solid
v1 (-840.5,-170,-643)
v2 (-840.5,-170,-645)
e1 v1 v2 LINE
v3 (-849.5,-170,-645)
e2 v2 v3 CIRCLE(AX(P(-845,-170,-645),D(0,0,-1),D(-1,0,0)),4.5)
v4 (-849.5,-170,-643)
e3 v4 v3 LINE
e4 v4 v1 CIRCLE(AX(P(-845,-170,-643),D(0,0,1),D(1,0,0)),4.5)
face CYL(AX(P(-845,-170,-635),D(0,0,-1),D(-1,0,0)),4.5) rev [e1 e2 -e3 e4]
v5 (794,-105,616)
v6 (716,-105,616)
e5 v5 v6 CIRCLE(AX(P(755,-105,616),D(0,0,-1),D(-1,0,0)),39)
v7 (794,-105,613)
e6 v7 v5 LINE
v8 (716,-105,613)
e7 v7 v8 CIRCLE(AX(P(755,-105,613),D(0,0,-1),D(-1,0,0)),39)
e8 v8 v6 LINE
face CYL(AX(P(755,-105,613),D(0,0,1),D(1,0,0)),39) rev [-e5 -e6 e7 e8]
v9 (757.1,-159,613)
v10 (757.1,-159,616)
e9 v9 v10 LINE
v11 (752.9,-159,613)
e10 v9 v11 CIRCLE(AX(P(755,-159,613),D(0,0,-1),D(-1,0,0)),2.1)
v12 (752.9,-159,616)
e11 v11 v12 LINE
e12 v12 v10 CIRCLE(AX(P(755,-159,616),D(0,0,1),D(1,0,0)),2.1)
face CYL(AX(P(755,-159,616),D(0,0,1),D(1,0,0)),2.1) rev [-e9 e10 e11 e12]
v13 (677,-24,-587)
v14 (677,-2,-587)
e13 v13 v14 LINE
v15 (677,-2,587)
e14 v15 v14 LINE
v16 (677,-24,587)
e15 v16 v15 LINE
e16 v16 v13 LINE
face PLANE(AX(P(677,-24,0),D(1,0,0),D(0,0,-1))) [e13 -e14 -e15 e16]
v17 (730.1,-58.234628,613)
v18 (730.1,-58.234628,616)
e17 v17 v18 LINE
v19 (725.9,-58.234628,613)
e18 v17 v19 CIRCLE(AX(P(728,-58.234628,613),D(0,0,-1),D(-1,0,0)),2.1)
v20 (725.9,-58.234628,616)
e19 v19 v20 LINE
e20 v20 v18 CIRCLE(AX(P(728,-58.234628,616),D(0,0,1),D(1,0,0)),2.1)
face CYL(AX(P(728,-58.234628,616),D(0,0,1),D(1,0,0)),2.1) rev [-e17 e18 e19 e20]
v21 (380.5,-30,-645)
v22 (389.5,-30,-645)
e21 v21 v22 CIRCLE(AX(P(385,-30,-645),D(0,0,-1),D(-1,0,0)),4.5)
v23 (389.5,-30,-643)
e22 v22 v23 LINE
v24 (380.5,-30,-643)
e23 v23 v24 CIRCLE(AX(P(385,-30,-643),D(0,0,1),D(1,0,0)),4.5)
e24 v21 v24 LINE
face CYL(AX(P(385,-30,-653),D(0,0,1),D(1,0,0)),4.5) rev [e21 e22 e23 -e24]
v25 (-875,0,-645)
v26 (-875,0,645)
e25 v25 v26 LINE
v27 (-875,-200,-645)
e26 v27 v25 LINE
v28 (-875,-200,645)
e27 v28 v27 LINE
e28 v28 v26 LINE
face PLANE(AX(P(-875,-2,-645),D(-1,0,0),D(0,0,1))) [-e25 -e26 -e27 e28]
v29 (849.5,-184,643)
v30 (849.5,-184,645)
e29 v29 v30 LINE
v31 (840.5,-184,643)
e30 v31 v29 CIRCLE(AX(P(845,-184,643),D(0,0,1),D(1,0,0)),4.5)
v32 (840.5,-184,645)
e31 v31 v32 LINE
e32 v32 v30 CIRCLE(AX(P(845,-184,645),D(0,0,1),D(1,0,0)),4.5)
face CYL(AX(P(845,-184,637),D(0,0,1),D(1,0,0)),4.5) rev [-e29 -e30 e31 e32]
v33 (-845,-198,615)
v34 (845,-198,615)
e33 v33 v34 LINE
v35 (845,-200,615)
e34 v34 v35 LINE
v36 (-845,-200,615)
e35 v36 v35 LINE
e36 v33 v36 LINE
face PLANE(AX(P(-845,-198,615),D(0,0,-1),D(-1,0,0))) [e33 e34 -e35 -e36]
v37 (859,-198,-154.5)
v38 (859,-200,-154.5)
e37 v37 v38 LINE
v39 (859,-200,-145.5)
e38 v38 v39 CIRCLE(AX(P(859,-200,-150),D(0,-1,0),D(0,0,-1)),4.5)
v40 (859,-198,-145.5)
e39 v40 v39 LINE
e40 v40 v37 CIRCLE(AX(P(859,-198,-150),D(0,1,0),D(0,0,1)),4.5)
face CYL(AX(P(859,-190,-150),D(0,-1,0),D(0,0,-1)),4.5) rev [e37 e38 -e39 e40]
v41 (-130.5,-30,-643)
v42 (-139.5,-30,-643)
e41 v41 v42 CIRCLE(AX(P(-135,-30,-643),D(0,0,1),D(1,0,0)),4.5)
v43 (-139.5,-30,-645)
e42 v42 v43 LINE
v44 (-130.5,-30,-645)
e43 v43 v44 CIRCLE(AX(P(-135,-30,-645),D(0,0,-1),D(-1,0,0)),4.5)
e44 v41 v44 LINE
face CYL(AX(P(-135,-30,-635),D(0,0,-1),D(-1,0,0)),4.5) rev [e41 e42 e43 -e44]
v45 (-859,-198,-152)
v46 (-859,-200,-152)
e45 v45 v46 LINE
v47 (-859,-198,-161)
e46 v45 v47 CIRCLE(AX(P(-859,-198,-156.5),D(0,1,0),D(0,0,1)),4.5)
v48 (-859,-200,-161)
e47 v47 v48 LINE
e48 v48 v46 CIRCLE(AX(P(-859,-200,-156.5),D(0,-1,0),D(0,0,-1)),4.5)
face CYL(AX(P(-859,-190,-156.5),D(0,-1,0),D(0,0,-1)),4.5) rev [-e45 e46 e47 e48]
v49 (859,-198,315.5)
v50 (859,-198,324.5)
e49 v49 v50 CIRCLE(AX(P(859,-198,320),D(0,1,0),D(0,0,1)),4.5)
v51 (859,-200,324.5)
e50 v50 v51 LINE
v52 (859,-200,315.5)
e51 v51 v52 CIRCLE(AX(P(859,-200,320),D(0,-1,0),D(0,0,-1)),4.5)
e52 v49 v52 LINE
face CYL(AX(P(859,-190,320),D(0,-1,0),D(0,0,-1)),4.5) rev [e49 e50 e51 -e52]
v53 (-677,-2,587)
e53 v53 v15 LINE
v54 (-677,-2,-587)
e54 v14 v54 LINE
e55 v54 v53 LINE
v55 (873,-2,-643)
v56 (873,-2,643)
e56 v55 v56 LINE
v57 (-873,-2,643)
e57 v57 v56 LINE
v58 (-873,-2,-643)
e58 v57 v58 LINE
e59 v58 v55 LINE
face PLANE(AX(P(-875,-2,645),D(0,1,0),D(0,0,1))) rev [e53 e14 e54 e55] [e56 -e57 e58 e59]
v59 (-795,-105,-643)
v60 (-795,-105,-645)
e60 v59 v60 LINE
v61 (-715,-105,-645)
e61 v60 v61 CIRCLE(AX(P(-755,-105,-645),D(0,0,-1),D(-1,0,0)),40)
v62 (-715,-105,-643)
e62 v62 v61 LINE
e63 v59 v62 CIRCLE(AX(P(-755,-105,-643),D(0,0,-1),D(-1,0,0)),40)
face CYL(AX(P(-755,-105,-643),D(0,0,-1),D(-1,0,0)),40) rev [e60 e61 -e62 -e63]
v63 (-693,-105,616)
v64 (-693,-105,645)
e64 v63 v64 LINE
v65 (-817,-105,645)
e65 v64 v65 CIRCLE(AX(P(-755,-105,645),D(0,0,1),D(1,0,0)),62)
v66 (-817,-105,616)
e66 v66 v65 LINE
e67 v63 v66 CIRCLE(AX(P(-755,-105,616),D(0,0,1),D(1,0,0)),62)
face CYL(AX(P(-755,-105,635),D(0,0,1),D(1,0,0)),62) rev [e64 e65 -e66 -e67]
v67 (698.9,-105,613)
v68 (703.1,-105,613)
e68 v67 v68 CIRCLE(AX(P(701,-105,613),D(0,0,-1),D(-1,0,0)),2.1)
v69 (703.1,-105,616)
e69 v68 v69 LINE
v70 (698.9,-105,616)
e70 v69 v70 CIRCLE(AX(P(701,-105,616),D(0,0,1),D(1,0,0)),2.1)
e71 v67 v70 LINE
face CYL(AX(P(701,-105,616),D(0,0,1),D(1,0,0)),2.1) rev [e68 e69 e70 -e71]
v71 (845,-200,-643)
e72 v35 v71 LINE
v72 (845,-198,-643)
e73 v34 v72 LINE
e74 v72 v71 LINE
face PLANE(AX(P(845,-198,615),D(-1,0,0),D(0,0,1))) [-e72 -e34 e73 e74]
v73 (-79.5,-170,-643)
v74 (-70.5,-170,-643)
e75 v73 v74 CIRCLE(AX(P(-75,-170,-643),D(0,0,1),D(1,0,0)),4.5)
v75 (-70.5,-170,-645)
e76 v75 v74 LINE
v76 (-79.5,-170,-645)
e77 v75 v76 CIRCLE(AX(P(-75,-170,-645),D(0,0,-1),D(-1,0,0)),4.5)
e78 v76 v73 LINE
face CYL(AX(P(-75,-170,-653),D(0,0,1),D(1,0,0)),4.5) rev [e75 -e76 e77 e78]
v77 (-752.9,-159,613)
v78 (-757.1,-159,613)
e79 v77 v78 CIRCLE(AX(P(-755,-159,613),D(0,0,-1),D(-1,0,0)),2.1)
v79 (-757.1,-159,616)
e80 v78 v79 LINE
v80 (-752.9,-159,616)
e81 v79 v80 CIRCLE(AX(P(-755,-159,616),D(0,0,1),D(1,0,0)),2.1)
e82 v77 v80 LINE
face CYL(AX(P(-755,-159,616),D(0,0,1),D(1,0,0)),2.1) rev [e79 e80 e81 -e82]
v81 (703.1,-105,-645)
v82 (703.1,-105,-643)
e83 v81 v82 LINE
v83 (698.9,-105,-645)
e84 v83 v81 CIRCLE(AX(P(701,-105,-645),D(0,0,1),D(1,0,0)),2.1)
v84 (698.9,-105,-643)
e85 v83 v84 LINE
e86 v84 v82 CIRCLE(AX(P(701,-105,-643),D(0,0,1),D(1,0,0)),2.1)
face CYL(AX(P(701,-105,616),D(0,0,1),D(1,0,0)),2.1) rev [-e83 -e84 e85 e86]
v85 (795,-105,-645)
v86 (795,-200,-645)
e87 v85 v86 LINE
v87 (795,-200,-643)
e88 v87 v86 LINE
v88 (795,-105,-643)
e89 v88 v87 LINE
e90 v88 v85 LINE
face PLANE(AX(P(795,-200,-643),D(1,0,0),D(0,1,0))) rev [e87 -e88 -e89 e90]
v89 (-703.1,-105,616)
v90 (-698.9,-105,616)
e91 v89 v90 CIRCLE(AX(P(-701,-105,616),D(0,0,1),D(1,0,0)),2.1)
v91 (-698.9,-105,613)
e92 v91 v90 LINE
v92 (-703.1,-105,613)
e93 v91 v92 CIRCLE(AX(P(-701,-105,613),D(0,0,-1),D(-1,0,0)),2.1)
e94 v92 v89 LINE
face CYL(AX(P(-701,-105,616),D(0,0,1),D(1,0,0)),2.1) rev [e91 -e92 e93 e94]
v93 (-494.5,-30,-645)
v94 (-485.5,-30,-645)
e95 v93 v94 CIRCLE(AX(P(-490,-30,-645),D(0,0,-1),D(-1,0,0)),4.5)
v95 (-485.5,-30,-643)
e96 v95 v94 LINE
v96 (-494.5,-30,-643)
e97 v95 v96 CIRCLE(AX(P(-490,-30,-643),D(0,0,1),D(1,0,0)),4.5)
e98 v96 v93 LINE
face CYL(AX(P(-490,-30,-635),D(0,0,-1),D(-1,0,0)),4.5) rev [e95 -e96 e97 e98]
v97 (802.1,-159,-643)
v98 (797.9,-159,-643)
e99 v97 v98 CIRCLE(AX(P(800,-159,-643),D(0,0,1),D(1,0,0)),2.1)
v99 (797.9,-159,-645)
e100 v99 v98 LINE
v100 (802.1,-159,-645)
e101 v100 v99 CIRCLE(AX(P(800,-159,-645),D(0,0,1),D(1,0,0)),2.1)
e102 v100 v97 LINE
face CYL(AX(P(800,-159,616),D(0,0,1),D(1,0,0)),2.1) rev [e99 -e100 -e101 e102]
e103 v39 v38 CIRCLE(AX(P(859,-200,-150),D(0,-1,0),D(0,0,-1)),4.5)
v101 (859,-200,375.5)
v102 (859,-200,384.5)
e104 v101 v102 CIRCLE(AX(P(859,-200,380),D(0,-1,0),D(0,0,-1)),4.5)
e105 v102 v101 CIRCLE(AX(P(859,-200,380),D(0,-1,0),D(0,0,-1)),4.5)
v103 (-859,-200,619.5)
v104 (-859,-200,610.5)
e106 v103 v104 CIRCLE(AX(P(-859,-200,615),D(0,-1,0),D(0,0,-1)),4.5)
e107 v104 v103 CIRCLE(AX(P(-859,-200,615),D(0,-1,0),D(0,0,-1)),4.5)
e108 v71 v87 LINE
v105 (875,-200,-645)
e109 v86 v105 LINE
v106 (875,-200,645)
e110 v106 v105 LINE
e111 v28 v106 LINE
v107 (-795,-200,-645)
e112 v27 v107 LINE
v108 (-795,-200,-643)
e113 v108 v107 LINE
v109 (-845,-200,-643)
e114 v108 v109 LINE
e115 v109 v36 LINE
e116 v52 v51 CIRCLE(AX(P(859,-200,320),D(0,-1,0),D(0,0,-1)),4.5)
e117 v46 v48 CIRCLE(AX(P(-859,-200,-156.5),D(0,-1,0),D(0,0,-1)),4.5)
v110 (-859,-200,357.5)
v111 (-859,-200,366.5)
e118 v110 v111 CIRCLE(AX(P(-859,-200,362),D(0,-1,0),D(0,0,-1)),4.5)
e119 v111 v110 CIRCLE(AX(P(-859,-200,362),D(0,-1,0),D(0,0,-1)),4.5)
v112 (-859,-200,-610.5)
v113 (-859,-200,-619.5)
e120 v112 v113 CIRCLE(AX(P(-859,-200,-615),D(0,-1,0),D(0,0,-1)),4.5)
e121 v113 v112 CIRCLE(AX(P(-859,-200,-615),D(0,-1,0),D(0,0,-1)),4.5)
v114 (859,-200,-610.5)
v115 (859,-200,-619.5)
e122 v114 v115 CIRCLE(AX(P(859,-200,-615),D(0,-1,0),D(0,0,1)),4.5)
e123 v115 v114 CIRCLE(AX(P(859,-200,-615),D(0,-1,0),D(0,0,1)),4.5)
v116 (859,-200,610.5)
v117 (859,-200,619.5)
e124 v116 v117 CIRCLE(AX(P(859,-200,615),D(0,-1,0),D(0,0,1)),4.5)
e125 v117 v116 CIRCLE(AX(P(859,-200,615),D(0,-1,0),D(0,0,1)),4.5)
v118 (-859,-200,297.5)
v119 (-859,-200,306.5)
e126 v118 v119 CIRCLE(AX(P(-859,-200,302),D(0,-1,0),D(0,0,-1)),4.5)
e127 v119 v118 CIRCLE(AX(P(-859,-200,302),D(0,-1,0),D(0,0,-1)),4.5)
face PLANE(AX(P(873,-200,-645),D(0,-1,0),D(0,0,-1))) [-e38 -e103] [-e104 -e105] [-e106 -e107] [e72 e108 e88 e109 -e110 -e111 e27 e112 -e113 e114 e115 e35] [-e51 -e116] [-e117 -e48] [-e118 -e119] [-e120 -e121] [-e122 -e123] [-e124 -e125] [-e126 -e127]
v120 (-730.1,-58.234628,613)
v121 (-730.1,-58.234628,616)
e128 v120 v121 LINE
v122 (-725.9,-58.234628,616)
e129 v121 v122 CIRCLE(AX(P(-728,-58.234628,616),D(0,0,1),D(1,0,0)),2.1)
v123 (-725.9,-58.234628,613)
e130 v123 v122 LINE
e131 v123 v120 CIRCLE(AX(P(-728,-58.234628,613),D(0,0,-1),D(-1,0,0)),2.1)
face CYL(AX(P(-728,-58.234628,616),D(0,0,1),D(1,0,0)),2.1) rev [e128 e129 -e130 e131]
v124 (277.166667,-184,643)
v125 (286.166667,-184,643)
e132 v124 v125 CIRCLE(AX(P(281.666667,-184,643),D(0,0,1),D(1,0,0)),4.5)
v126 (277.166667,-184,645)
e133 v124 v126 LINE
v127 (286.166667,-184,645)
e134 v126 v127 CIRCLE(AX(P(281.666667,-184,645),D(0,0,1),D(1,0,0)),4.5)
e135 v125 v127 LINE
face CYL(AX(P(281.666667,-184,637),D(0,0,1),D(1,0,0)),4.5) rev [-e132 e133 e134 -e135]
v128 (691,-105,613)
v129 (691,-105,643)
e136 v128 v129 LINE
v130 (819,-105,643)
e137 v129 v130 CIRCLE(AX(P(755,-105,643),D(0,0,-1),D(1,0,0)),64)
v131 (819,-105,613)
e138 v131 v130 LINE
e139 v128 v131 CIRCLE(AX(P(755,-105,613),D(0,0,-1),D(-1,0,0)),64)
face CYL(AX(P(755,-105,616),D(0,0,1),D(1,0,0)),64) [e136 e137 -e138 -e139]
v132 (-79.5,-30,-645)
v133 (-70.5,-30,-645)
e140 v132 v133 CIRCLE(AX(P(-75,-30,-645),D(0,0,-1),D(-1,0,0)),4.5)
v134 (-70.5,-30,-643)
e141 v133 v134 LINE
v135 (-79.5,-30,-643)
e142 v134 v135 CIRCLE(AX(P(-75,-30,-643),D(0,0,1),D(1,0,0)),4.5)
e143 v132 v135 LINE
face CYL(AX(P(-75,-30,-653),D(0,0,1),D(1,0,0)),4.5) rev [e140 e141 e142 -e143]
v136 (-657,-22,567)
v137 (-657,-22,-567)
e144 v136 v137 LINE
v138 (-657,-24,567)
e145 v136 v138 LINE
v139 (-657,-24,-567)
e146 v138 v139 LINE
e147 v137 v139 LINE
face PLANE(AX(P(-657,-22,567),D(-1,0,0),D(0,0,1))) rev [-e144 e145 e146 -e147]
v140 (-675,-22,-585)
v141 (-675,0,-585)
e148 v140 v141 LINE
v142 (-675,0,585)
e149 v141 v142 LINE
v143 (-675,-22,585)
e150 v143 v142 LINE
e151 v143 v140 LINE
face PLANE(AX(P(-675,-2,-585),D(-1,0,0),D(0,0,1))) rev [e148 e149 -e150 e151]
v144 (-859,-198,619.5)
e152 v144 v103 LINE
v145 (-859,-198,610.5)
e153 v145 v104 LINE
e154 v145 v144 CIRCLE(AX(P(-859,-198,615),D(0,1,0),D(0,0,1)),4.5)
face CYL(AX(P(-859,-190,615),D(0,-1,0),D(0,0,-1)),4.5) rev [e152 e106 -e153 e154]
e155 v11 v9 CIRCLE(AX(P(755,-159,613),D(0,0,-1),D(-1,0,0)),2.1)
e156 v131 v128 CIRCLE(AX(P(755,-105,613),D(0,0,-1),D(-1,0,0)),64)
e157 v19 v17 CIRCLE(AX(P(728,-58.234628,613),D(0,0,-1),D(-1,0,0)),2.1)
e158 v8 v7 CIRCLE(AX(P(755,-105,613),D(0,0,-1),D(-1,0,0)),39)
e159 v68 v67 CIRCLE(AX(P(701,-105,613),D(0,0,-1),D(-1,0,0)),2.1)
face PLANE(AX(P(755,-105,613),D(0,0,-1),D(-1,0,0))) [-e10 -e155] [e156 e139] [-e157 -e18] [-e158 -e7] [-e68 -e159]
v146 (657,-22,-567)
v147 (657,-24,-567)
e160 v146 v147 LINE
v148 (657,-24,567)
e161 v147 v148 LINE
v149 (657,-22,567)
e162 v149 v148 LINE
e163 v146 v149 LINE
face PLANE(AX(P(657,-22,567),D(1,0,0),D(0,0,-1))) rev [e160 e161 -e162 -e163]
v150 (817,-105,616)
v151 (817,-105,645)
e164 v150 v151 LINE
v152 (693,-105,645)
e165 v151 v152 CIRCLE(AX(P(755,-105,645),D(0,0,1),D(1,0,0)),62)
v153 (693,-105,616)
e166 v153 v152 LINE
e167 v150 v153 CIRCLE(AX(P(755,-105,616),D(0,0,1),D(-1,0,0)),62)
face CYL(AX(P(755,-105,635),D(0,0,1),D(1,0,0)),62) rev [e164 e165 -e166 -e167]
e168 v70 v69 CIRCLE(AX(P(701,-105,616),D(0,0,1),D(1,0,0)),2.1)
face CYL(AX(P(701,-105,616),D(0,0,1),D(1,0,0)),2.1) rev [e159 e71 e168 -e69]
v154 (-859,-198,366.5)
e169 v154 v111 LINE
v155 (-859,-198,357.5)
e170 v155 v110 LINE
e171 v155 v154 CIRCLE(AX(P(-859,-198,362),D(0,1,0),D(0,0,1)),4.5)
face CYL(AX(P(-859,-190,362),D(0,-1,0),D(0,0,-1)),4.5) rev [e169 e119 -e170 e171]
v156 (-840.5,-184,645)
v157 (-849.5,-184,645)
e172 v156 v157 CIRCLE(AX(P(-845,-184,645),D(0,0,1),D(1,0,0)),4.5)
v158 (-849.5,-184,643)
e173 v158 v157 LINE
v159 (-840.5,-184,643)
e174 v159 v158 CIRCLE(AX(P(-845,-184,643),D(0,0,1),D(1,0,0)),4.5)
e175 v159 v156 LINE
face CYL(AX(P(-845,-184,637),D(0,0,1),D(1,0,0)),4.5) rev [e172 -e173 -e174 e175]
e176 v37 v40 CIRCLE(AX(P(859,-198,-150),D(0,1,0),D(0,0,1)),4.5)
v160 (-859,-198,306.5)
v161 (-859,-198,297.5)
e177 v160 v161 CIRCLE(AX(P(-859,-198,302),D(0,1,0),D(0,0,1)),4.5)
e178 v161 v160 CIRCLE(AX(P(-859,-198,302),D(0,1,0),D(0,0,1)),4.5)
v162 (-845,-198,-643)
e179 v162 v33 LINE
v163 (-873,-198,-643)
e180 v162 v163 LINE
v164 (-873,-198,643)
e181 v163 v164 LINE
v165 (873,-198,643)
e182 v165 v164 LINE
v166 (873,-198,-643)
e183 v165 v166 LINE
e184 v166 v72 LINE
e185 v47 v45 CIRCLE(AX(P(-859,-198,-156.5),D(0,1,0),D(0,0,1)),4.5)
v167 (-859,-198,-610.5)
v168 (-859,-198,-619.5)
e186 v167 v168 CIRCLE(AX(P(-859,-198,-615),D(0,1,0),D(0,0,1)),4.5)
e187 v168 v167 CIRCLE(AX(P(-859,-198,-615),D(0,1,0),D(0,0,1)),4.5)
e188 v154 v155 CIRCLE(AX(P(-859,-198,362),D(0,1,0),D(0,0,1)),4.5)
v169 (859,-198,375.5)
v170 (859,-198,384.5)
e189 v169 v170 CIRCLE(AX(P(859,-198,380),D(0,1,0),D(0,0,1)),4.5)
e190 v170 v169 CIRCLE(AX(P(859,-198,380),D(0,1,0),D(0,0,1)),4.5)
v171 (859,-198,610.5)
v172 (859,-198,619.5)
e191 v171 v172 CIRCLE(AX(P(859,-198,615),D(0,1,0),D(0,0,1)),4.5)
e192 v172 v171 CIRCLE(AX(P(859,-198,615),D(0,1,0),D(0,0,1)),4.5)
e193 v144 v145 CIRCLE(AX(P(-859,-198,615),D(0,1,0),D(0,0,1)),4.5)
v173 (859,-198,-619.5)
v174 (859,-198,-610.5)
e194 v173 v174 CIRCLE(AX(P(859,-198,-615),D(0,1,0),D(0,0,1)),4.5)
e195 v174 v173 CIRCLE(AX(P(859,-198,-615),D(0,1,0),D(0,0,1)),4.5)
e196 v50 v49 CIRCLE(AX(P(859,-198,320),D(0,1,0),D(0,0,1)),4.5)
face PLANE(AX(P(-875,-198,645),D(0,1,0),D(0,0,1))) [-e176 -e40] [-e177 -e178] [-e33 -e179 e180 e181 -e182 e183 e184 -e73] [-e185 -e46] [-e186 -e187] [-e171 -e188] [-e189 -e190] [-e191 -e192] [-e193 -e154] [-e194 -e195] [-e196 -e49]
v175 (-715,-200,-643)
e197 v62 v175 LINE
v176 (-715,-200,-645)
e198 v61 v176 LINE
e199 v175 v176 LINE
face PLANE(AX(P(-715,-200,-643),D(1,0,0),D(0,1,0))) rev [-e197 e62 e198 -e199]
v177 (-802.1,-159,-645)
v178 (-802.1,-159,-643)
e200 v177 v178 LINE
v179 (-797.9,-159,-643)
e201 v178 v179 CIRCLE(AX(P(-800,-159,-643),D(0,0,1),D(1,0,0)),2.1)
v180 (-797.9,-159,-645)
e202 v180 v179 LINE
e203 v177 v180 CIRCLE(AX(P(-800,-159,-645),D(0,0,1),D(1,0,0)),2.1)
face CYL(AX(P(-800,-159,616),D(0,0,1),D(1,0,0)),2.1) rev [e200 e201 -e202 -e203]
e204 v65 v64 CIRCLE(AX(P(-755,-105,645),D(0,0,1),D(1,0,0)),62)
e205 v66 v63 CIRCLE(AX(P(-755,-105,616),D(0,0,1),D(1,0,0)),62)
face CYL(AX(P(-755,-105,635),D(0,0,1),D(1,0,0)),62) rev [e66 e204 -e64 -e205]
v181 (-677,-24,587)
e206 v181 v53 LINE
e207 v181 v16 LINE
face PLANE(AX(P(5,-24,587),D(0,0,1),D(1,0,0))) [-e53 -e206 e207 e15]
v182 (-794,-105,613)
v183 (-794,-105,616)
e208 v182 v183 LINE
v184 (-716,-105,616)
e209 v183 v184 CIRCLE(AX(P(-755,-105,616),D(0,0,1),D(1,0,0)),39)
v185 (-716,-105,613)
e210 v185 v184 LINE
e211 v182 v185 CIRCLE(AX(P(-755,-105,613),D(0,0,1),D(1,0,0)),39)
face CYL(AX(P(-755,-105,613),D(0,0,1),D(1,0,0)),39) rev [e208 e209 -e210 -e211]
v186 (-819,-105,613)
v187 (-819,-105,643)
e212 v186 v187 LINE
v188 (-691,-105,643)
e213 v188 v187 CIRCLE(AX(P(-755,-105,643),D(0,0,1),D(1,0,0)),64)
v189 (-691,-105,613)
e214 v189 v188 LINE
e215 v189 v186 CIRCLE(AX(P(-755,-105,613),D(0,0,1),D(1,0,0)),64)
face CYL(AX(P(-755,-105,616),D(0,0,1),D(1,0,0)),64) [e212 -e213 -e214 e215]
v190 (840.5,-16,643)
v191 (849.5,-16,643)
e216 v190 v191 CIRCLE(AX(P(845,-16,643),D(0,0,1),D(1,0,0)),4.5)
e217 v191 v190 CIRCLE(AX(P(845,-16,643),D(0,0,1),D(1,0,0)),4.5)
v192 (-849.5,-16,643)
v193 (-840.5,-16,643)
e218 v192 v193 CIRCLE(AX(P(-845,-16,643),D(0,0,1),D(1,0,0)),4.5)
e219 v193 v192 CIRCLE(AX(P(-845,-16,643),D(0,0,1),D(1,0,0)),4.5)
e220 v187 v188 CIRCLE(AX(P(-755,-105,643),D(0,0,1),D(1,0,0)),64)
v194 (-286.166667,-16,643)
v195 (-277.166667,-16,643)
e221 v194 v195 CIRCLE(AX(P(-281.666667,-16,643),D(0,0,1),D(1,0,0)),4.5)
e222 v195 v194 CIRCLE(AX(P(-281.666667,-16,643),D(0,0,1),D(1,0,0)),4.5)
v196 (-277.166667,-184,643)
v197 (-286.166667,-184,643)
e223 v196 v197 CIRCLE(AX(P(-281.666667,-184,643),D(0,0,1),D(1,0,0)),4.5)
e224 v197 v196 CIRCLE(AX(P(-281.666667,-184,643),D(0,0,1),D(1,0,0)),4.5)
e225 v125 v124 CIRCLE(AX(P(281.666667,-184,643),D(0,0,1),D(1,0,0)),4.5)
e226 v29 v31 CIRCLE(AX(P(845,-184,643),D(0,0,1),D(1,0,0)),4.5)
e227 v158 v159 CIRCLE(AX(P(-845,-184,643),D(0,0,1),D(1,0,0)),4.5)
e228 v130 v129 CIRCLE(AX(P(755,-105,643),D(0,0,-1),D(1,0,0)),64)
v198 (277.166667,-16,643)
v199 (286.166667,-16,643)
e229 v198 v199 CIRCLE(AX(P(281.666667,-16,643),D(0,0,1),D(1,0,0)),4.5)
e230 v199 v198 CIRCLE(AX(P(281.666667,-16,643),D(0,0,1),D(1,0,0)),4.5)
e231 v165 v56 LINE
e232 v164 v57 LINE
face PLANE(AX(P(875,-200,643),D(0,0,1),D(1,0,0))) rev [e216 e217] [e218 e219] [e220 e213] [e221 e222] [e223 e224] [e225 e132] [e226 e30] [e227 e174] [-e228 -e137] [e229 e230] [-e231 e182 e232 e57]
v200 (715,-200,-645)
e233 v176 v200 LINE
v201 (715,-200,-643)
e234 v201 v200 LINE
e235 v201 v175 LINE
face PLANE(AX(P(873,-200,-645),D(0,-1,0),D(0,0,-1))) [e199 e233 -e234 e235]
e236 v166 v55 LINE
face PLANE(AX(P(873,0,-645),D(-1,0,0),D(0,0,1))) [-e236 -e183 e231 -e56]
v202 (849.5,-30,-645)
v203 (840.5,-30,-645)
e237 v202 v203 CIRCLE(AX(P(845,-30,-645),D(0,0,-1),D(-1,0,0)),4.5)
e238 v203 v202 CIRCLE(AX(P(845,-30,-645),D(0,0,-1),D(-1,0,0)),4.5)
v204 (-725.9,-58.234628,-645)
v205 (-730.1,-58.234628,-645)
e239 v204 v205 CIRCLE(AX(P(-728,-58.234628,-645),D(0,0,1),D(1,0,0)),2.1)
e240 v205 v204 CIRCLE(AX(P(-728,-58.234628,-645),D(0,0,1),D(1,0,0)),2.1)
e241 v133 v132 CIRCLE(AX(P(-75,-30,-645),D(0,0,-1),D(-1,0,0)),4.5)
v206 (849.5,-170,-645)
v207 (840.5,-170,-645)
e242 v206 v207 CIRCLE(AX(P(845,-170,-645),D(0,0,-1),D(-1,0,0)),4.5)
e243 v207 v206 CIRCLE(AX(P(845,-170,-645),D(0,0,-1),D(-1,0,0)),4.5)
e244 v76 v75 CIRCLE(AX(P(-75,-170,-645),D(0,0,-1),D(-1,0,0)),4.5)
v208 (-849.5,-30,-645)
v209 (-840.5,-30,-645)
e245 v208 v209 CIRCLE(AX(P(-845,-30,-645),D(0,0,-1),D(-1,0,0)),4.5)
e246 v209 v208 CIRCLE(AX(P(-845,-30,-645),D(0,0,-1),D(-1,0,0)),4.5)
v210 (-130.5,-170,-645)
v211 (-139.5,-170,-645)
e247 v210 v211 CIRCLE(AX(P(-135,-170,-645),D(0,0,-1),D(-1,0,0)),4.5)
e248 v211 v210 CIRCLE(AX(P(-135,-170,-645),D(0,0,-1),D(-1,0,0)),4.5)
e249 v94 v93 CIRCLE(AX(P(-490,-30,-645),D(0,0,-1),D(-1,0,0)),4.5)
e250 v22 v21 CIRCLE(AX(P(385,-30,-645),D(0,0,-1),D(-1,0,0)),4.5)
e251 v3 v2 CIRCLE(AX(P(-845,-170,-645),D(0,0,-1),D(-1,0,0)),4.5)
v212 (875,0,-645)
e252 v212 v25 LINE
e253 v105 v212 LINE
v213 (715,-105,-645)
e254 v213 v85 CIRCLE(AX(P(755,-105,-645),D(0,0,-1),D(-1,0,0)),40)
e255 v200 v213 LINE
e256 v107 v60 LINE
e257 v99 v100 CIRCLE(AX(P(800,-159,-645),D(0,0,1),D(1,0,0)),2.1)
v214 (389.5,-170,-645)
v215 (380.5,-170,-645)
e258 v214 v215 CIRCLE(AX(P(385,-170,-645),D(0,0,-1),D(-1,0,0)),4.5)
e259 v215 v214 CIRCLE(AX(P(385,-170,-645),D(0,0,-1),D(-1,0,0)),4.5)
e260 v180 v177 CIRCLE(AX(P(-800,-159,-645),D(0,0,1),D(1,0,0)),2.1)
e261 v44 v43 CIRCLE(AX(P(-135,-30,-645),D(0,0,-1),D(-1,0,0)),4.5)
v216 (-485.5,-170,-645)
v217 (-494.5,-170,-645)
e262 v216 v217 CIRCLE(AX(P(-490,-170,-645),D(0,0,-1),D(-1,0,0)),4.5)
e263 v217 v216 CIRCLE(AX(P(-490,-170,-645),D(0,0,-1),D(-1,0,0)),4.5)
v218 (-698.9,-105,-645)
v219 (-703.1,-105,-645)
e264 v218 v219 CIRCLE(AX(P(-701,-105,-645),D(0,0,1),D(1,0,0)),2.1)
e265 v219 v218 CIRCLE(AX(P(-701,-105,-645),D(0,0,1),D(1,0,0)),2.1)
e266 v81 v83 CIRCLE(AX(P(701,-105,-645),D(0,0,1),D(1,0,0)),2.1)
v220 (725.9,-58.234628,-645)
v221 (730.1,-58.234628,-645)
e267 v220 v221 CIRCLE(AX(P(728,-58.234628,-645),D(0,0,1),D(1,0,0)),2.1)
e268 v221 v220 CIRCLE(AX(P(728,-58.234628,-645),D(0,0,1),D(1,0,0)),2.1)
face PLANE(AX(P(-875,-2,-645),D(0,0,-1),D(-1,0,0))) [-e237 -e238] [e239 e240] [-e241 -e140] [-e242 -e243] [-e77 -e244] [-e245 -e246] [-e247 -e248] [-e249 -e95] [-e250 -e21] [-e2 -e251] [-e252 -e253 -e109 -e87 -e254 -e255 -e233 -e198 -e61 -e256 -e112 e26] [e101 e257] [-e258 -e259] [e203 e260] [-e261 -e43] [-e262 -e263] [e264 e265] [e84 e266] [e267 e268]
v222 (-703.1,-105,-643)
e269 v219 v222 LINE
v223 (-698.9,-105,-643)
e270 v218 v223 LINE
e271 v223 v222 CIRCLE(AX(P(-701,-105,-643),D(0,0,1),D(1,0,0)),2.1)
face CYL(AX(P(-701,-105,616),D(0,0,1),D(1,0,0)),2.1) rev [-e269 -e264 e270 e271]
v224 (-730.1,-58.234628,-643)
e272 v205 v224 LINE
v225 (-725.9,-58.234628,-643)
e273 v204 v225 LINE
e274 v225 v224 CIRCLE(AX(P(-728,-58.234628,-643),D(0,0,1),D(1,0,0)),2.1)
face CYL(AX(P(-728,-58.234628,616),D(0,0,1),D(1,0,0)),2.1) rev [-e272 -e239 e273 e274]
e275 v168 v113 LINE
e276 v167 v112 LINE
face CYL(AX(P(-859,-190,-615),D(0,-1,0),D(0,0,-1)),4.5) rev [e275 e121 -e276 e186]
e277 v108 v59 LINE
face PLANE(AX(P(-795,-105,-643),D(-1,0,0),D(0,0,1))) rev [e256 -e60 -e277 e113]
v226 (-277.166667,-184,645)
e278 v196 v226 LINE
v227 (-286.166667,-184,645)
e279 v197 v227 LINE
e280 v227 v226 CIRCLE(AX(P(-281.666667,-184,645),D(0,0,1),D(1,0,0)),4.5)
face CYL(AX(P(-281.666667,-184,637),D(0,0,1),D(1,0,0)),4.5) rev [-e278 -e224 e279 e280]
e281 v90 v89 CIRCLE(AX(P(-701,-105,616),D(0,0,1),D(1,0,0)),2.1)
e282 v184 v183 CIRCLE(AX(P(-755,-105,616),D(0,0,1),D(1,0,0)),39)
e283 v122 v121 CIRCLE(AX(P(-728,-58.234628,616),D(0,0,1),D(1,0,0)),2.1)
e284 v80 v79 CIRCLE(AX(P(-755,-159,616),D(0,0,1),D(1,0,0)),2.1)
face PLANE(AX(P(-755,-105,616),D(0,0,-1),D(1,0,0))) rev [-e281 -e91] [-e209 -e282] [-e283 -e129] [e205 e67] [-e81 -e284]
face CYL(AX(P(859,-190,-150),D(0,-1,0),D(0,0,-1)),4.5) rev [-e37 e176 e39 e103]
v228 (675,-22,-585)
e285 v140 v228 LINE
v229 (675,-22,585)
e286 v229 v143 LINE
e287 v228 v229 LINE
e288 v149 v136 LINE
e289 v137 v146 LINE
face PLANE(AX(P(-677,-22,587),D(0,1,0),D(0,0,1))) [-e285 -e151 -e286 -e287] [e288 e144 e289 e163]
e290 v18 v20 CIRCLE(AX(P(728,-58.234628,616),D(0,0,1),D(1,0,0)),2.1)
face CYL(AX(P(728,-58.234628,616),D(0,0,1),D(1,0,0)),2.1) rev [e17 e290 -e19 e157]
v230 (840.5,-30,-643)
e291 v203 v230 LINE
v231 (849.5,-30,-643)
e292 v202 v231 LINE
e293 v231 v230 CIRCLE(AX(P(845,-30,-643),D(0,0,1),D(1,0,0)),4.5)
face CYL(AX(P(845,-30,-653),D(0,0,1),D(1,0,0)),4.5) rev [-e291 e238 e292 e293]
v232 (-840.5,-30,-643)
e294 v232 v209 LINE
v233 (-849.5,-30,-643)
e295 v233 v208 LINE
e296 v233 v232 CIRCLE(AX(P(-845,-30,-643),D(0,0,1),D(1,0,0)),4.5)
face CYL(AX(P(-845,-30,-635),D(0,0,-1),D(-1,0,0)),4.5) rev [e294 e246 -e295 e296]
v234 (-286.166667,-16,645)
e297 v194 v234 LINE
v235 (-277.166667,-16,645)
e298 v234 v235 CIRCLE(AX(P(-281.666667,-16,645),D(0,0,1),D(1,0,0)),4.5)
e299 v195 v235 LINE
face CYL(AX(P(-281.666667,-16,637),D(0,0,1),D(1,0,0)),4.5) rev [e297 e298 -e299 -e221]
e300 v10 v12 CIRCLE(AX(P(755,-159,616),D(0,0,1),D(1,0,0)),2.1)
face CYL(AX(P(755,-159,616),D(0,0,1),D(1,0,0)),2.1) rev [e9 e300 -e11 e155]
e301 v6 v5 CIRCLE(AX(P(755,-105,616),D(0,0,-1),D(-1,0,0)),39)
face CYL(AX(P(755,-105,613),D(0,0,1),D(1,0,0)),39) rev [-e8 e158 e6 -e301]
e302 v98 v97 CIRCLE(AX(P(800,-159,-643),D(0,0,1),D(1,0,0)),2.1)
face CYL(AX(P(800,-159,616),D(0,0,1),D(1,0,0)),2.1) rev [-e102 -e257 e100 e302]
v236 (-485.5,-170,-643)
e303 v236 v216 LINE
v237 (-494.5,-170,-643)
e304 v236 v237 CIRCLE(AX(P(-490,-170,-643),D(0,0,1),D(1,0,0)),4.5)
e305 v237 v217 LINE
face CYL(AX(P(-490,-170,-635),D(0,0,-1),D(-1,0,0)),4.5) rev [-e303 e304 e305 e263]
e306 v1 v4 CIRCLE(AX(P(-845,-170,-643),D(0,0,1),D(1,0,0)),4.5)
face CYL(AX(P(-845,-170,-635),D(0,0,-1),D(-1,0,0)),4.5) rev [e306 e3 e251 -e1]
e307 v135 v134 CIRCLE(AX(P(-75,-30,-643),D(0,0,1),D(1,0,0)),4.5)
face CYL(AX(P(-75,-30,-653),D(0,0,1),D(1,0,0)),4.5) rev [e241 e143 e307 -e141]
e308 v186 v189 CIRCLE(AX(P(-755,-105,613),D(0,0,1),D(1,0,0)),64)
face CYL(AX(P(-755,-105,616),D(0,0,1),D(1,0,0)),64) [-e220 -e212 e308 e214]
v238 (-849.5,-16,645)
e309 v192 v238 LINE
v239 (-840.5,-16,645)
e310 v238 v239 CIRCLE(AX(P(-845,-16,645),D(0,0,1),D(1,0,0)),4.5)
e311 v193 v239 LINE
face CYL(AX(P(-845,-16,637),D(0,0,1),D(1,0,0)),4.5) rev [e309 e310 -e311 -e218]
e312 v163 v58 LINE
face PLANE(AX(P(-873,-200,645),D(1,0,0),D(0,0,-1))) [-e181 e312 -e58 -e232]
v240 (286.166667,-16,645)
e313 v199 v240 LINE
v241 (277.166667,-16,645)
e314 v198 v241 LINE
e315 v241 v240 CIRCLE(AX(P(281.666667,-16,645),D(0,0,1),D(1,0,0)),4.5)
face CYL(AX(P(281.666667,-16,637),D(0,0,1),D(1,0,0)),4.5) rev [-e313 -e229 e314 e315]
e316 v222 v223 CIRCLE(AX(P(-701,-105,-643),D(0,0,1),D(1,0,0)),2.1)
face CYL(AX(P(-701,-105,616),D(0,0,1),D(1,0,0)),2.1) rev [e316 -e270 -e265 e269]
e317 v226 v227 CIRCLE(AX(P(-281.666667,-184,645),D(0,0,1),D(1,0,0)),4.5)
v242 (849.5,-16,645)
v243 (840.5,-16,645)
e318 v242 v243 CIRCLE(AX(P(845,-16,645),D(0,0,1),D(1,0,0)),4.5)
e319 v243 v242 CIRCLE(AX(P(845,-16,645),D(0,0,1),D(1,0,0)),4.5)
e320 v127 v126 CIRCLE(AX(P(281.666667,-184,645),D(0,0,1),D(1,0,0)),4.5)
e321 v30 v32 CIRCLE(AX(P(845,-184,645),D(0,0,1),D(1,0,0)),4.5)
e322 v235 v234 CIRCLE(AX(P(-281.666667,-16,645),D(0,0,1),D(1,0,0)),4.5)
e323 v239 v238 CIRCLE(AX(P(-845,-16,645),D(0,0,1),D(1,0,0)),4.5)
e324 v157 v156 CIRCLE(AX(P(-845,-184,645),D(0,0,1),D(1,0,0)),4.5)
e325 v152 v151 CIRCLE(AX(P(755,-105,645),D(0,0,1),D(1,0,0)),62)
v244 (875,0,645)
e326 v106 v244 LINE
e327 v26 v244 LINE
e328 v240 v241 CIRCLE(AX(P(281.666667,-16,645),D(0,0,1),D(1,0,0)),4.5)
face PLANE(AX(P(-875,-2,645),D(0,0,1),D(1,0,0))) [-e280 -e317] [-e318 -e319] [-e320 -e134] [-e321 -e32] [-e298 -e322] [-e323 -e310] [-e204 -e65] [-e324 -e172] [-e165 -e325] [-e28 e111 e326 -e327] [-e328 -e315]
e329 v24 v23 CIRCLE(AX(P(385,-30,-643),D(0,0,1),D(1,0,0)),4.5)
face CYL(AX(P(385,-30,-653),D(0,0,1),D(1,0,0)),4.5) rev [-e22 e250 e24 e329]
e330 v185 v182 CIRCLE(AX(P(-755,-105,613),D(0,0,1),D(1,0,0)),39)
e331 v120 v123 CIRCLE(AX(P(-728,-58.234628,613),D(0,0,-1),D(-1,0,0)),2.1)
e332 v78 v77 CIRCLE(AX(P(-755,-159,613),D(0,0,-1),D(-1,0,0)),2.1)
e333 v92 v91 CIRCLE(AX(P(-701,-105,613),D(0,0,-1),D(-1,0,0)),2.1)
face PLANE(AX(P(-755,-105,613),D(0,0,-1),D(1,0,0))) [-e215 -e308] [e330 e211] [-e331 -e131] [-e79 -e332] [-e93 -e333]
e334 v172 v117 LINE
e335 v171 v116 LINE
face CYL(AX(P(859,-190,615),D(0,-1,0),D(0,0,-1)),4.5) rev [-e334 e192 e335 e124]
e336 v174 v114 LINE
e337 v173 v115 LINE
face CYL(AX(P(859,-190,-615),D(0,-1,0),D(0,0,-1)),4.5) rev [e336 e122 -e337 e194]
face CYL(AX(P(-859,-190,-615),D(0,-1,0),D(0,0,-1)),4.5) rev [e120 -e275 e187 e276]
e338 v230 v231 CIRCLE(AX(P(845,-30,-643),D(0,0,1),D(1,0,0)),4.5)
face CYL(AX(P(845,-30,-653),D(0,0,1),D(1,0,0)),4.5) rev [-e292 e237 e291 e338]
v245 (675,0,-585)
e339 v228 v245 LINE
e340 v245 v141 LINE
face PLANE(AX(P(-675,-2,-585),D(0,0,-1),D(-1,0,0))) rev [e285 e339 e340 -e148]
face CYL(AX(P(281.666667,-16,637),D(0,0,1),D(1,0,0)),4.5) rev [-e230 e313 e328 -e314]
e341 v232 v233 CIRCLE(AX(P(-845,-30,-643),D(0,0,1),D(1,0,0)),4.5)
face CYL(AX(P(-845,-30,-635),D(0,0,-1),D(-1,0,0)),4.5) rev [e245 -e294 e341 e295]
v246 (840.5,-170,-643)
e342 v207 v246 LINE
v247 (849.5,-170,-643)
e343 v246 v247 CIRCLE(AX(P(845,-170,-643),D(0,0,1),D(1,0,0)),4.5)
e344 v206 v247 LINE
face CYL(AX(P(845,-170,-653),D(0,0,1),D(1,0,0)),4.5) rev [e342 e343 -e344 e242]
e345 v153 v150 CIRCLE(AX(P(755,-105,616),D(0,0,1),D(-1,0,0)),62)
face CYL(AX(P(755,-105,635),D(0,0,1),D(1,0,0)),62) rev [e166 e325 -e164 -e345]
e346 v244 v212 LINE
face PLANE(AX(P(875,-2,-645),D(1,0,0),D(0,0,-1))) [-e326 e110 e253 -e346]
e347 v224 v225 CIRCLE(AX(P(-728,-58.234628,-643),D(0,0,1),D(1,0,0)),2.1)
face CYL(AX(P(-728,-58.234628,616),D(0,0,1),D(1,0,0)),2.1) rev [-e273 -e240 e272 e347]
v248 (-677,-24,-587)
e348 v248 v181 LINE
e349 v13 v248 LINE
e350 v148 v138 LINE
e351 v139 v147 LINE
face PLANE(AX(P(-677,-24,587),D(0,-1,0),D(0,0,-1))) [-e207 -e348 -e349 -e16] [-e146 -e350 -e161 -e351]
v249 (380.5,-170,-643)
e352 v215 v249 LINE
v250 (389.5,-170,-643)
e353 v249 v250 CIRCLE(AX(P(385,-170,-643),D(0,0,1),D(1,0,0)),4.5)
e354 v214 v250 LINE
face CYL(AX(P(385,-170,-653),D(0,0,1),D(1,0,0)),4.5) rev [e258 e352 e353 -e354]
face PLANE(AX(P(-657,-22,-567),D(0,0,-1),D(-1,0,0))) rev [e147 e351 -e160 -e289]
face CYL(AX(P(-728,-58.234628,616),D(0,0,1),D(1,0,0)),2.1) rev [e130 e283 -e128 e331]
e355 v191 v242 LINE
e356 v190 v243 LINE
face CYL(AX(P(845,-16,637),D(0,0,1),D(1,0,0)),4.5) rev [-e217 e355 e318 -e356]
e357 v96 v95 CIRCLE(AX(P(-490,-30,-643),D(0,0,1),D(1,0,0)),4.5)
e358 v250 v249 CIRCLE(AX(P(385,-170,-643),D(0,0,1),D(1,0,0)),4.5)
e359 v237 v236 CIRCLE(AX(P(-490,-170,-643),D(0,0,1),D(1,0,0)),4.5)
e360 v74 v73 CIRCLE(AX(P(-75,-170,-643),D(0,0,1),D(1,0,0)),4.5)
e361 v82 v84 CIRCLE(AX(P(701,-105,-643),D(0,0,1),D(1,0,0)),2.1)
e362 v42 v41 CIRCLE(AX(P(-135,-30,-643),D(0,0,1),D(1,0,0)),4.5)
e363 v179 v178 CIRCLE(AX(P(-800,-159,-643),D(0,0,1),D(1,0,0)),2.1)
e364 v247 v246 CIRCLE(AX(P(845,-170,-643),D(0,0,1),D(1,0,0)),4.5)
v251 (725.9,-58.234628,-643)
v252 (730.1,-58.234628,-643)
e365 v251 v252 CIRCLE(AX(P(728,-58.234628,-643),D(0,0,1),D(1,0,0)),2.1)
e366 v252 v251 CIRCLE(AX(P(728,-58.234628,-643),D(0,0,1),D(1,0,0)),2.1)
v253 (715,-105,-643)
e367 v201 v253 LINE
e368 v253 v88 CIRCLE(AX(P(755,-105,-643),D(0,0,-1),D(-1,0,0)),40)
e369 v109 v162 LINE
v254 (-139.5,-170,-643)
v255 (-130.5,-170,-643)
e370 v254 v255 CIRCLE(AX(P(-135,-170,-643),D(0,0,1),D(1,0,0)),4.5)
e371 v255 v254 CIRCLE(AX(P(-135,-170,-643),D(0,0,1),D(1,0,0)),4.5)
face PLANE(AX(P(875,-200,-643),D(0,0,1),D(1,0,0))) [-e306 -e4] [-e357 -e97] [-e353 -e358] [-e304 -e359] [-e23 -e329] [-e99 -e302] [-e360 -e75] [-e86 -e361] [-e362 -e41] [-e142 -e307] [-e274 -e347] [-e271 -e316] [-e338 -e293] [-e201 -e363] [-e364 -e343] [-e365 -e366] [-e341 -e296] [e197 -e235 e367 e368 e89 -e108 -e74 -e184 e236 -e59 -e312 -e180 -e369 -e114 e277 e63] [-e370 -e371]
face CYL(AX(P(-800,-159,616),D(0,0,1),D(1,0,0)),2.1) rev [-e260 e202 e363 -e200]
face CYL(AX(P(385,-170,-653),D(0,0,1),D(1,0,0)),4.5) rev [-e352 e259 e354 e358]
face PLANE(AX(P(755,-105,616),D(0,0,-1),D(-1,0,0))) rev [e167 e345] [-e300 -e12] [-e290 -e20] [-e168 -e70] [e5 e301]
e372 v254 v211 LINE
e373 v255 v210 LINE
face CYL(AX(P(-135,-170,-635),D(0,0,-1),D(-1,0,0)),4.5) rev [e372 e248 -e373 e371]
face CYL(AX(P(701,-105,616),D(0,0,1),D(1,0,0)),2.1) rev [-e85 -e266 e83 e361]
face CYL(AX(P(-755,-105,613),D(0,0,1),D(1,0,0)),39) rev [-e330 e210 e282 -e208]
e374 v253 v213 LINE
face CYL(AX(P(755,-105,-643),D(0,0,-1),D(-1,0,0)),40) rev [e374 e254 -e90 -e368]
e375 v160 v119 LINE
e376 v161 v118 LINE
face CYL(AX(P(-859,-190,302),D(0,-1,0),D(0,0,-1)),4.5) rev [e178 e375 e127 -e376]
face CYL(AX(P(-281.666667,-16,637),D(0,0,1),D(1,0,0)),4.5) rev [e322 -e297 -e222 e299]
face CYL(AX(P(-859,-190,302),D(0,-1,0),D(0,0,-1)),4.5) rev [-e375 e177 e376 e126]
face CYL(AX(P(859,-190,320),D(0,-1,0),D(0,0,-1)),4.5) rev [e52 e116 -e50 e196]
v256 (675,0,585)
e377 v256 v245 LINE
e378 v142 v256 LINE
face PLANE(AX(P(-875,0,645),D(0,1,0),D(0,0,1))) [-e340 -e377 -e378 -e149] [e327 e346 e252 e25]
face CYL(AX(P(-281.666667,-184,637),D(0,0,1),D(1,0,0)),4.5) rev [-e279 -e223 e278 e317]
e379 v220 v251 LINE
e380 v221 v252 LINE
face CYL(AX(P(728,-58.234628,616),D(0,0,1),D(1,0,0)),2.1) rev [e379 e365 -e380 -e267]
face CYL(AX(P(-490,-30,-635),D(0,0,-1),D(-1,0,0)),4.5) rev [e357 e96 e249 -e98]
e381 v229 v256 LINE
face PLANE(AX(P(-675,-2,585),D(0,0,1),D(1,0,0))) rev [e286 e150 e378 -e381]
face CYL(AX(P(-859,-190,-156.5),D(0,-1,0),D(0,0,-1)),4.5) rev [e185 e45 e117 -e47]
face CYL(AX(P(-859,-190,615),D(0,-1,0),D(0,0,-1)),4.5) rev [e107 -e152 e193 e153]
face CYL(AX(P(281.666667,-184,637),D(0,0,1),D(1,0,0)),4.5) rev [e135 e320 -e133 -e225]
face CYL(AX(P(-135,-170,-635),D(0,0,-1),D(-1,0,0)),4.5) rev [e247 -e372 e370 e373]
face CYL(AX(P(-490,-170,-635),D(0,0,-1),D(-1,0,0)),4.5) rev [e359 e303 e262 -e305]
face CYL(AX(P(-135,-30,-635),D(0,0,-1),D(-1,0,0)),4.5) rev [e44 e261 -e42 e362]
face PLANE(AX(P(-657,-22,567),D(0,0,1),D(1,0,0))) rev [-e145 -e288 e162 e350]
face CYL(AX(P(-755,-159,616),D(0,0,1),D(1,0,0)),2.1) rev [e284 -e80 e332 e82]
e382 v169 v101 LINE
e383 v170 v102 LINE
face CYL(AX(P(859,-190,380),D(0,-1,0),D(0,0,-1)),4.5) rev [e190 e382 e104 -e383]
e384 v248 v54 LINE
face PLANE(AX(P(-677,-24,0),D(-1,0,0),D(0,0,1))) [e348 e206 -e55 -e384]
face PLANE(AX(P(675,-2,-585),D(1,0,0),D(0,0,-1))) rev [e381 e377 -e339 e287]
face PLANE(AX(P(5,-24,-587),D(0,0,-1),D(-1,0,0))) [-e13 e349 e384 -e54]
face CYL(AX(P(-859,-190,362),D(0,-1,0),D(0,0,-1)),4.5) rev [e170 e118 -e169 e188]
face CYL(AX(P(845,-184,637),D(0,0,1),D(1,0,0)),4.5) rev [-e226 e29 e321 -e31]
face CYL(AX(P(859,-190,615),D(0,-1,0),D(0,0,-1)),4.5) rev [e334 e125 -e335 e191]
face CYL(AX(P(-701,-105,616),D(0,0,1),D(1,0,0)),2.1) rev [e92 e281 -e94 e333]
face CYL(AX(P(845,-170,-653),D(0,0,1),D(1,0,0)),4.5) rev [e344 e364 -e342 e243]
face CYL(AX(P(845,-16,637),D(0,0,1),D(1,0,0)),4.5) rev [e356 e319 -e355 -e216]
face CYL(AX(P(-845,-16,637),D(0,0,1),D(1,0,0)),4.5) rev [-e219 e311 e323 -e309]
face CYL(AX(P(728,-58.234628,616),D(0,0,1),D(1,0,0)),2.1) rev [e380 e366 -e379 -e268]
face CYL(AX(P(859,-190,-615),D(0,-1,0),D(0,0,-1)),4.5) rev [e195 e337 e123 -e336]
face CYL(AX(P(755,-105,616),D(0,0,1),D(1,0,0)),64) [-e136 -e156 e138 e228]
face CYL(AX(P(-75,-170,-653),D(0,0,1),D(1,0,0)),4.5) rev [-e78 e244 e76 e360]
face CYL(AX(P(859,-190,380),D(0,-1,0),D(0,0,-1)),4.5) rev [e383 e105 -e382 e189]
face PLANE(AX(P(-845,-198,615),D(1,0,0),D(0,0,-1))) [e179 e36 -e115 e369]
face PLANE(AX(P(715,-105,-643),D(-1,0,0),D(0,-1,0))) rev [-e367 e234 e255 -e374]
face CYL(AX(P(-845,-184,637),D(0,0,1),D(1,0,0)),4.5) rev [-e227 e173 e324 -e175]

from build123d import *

# Parameters (mm, degrees)
SKETCH_1_W                  = 1750
SKETCH_1_H                  = 1290
EXTRUDE_1_DEPTH             = 2
SKETCH_2_W                  = 1350
SKETCH_2_H                  = 1170
CUT_EXTRUDE_1_DEPTH         = 2
SKETCH_3_W                  = 1290
SKETCH_3_H                  = 200
EXTRUDE_2_DEPTH             = 2
SKETCH_4_W                  = 1750
SKETCH_4_H                  = 200
EXTRUDE_3_DEPTH             = 2
SKETCH_5_W                  = 1750
SKETCH_5_H                  = 200
EXTRUDE_4_DEPTH             = 2
SKETCH_6_W                  = 1290
SKETCH_6_H                  = 200
EXTRUDE_5_DEPTH             = 2
SKETCH_7_W                  = 1350
SKETCH_7_H                  = 1170
EXTRUDE_6_DEPTH             = 24
SKETCH_8_W                  = 1354
SKETCH_8_H                  = 1174
SKETCH_8_W_2                = 1314
SKETCH_8_H_2                = 1134
EXTRUDE_7_DEPTH             = 2
EXTRUDE_8_DEPTH             = 2
CUT_EXTRUDE_2_DEPTH         = 2
SKETCH_11_R                 = 4.5
CUT_EXTRUDE_3_DEPTH         = 10
SKETCH_12_R                 = 4.5
CUT_EXTRUDE_4_DEPTH         = 10
SKETCH_13_R                 = 4.5
CUT_EXTRUDE_5_DEPTH         = 10
SKETCH_14_R                 = 4.5
CUT_EXTRUDE_6_DEPTH         = 8
SKETCH_16_R                 = 62
CUT_EXTRUDE_7_DEPTH         = 10
SKETCH_17_R                 = 64
SKETCH_17_R_2               = 62
EXTRUDE_9_DEPTH             = 27
SKETCH_22_R                 = 64
SKETCH_22_R_2               = 39
EXTRUDE_11_DEPTH            = 3
SKETCH_23_W                 = 2.1
SKETCH_23_H                 = 1261
HOLE_WIZARD_M5_1_AT_2_COUNT = 2
HOLE_WIZARD_M5_1_AT_2_PITCH = 54
HOLE_WIZARD_M5_1_AT_3_COUNT = 2
HOLE_WIZARD_M5_1_AT_3_PITCH = 104.319989239
HOLE_WIZARD_M5_1_AT_4_COUNT = 2
HOLE_WIZARD_M5_1_AT_4_PITCH = 123.845307359
MIRROR_3_COPY_1_SKETCH_W    = 2.1
MIRROR_3_COPY_1_SKETCH_H    = 1261
MIRROR_3_COPY_2_SKETCH_W    = 2.1
MIRROR_3_COPY_2_SKETCH_H    = 1261
MIRROR_3_COPY_3_SKETCH_W    = 2.1
MIRROR_3_COPY_3_SKETCH_H    = 1261


with BuildPart() as part:
    # 草图1 → 凸台-拉伸1 (new body)
    with BuildSketch(Plane(origin=(0, 0, 0), x_dir=(1, 0, 0), z_dir=(0, 1, 0))):
        Rectangle(SKETCH_1_W, SKETCH_1_H)
    extrude(amount=-EXTRUDE_1_DEPTH)

    # 草图2 → 切除-拉伸1 (cut)
    with BuildSketch(Plane(origin=(0, 0, 0), x_dir=(-1, 0, 0), z_dir=(0, 1, 0))):
        Rectangle(SKETCH_2_W, SKETCH_2_H)
    extrude(amount=-CUT_EXTRUDE_1_DEPTH, mode=Mode.SUBTRACT)

    # 草图3 → 凸台-拉伸2 (add)
    with BuildSketch(Plane(origin=(875, 0, 0), x_dir=(0, 0, -1), z_dir=(1, 0, 0))):
        with Locations((0, -100)):
            Rectangle(SKETCH_3_W, SKETCH_3_H)
    extrude(amount=-EXTRUDE_2_DEPTH)

    # 草图4 → 凸台-拉伸3 (add)
    with BuildSketch(Plane(origin=(0, 0, -645), x_dir=(-1, 0, 0), z_dir=(0, 0, -1))):
        with Locations((0, -100)):
            Rectangle(SKETCH_4_W, SKETCH_4_H)
    extrude(amount=-EXTRUDE_3_DEPTH)

    # 草图5 → 凸台-拉伸4 (add)
    with BuildSketch(Plane.XY.offset(645)):
        with Locations((0, -100)):
            Rectangle(SKETCH_5_W, SKETCH_5_H)
    extrude(amount=-EXTRUDE_4_DEPTH)

    # 草图6 → 凸台-拉伸5 (add)
    with BuildSketch(Plane.ZY.offset(875)):
        with Locations((0, -100)):
            Rectangle(SKETCH_6_W, SKETCH_6_H)
    extrude(amount=-EXTRUDE_5_DEPTH)

    # 草图7 → 凸台-拉伸6 (add)
    with BuildSketch(Plane(origin=(0, 0, 0), x_dir=(1, 0, 0), z_dir=(0, 1, 0))):
        Polygon((-677, 0), (-677, 587), (5, 587), (677, 587), (677, 0), (677, -587), (5, -587), (-677, -587), align=None)
        Rectangle(SKETCH_7_W, SKETCH_7_H, mode=Mode.SUBTRACT)
    extrude(amount=-EXTRUDE_6_DEPTH)

    # 草图8 → 凸台-拉伸7 (add)
    with BuildSketch(Plane.XZ.offset(24)):
        Rectangle(SKETCH_8_W, SKETCH_8_H)
        Rectangle(SKETCH_8_W_2, SKETCH_8_H_2, mode=Mode.SUBTRACT)
    extrude(amount=-EXTRUDE_7_DEPTH)

    # 草图9 → 凸台-拉伸8 (add)
    with BuildSketch(Plane.XZ.offset(200)):
        Polygon((-875, 645), (875, 645), (875, -645), (845, -645), (845, 615), (-845, 615), (-845, -610), (-845, -645), (-875, -645), align=None)
    extrude(amount=-EXTRUDE_8_DEPTH)

    # 草图10 → 切除-拉伸2 (cut)
    with BuildSketch(Plane(origin=(0, 0, -645), x_dir=(-1, 0, 0), z_dir=(0, 0, -1))):
        with BuildLine():
            Line((-795, -200), (-795, -105))
            ThreePointArc((-795, -105), (-755, -65), (-715, -105))
            Line((-715, -105), (-715, -200))
            Line((-715, -200), (-795, -200))
        make_face()
        with BuildLine():
            Line((715, -200), (715, -105))
            ThreePointArc((715, -105), (755, -65), (795, -105))
            Line((795, -105), (795, -200))
            Line((795, -200), (715, -200))
        make_face()
    extrude(amount=-CUT_EXTRUDE_2_DEPTH, mode=Mode.SUBTRACT)

    # 草图11 → 切除-拉伸3 (cut)
    with BuildSketch(Plane.XY.offset(-643)):
        with Locations((845, -30)):
            Circle(SKETCH_11_R)
        with Locations((845, -170)):
            Circle(SKETCH_11_R)
        with Locations((385, -30)):
            Circle(SKETCH_11_R)
        with Locations((385, -170)):
            Circle(SKETCH_11_R)
        with Locations((-75, -30)):
            Circle(SKETCH_11_R)
        with Locations((-75, -170)):
            Circle(SKETCH_11_R)
    extrude(amount=-CUT_EXTRUDE_3_DEPTH, mode=Mode.SUBTRACT)

    # 草图12 → 切除-拉伸4 (cut)
    with BuildSketch(Plane(origin=(0, 0, -645), x_dir=(-1, 0, 0), z_dir=(0, 0, -1))):
        with Locations((845, -30)):
            Circle(SKETCH_12_R)
        with Locations((845, -170)):
            Circle(SKETCH_12_R)
        with Locations((490, -30)):
            Circle(SKETCH_12_R)
        with Locations((490, -170)):
            Circle(SKETCH_12_R)
        with Locations((135, -30)):
            Circle(SKETCH_12_R)
        with Locations((135, -170)):
            Circle(SKETCH_12_R)
    extrude(amount=-CUT_EXTRUDE_4_DEPTH, mode=Mode.SUBTRACT)

    # 草图13 → 切除-拉伸5 (cut)
    with BuildSketch(Plane.XZ.offset(200)):
        with Locations(Location((-859, 615, 0), (0, 0, 270))):
            Circle(SKETCH_13_R)
        with Locations(Location((-859, -615, 0), (0, 0, 270))):
            Circle(SKETCH_13_R)
        with Locations(Location((859, -615, 0), (0, 0, 90))):
            Circle(SKETCH_13_R)
        with Locations(Location((859, 615, 0), (0, 0, 90))):
            Circle(SKETCH_13_R)
        with Locations(Location((859, 320, 0), (0, 0, 270))):
            Circle(SKETCH_13_R)
        with Locations(Location((859, -150, 0), (0, 0, 270))):
            Circle(SKETCH_13_R)
        with Locations(Location((-859, 302, 0), (0, 0, 270))):
            Circle(SKETCH_13_R)
        with Locations(Location((-859, -156.5, 0), (0, 0, 270))):
            Circle(SKETCH_13_R)
        with Locations(Location((-859, 362, 0), (0, 0, 270))):
            Circle(SKETCH_13_R)
        with Locations(Location((859, 380, 0), (0, 0, 270))):
            Circle(SKETCH_13_R)
    extrude(amount=-CUT_EXTRUDE_5_DEPTH, mode=Mode.SUBTRACT)

    # 草图14 → 切除-拉伸6 (cut)
    with BuildSketch(Plane.XY.offset(645)):
        with Locations((-845, -16)):
            Circle(SKETCH_14_R)
        with Locations((-281.666666667, -16)):
            Circle(SKETCH_14_R)
        with Locations((281.666666667, -16)):
            Circle(SKETCH_14_R)
        with Locations((845, -16)):
            Circle(SKETCH_14_R)
        with Locations((-845, -184)):
            Circle(SKETCH_14_R)
        with Locations((-281.666666667, -184)):
            Circle(SKETCH_14_R)
        with Locations((281.666666667, -184)):
            Circle(SKETCH_14_R)
        with Locations((845, -184)):
            Circle(SKETCH_14_R)
    extrude(amount=-CUT_EXTRUDE_6_DEPTH, mode=Mode.SUBTRACT)

    # 草图16 → 切除-拉伸7 (cut)
    with BuildSketch(Plane.XY.offset(645)):
        with Locations((755, -105)):
            Circle(SKETCH_16_R)
        with Locations((-755, -105)):
            Circle(SKETCH_16_R)
    extrude(amount=-CUT_EXTRUDE_7_DEPTH, mode=Mode.SUBTRACT)

    # 草图17 → 凸台-拉伸9 (add)
    with BuildSketch(Plane(origin=(0, 0, 643), x_dir=(-1, 0, 0), z_dir=(0, 0, -1))):
        with Locations(Location((-755, -105, 0), (0, 0, 180))):
            Circle(SKETCH_17_R)
        with Locations(Location((-755, -105, 0), (0, 0, 180))):
            Circle(SKETCH_17_R_2, mode=Mode.SUBTRACT)
    extrude_9 = extrude(amount=EXTRUDE_9_DEPTH)

    # 草图22 → 凸台-拉伸11 (add)
    with BuildSketch(Plane(origin=(0, 0, 616), x_dir=(-1, 0, 0), z_dir=(0, 0, -1))):
        with Locations(Location((-755, -105, 0), (0, 0, 180))):
            Circle(SKETCH_22_R)
        with Locations((-755, -105)):
            Circle(SKETCH_22_R_2, mode=Mode.SUBTRACT)
    extrude_11 = extrude(amount=EXTRUDE_11_DEPTH)

    # 镜向2: 凸台-拉伸9, 凸台-拉伸11 across plane
    add(extrude_9.mirror(Plane.ZY))
    add(extrude_11.mirror(Plane.ZY))

    # 草图23 → M5 螺纹孔1 (revolve, cut)
    with BuildSketch(Plane(origin=(728, -58.234628196, 616), x_dir=(0, -1, 0), z_dir=(1, 0, 0))):
        with Locations((1.05, 630.5)):
            Rectangle(SKETCH_23_W, SKETCH_23_H)
    hole_wizard_m5_1 = revolve(axis=Axis((728, -58.234628196, 622.35), (0, 0, -1)), mode=Mode.SUBTRACT)

    # M5 螺纹孔1 at 2: M5 螺纹孔1 ×2
    with Locations(*[Vector(-0.5000000000000002, -0.8660254037844386, 0) * (i * HOLE_WIZARD_M5_1_AT_2_PITCH) for i in range(1, HOLE_WIZARD_M5_1_AT_2_COUNT)]):
        add(hole_wizard_m5_1, mode=Mode.SUBTRACT)

    # M5 螺纹孔1 at 3: M5 螺纹孔1 ×2
    with Locations(*[Vector(0.25881904510252085, -0.9659258262890683, 0) * (i * HOLE_WIZARD_M5_1_AT_3_PITCH) for i in range(1, HOLE_WIZARD_M5_1_AT_3_COUNT)]):
        add(hole_wizard_m5_1, mode=Mode.SUBTRACT)

    # M5 螺纹孔1 at 4: M5 螺纹孔1 ×2
    with Locations(*[Vector(0.5813704332876158, -0.8136389981428925, 0) * (i * HOLE_WIZARD_M5_1_AT_4_PITCH) for i in range(1, HOLE_WIZARD_M5_1_AT_4_COUNT)]):
        add(hole_wizard_m5_1, mode=Mode.SUBTRACT)

    # 镜向3: M5 螺纹孔1 across plane
    add(hole_wizard_m5_1.mirror(Plane.ZY), mode=Mode.SUBTRACT)

    # 镜向3 copy 1 sketch → 镜向3 copy 1 (revolve, cut)
    with BuildSketch(Plane(origin=(-701, -105, 616), x_dir=(0, -1, 0), z_dir=(-1, 0, 0))):
        with Locations((1.05, -630.5)):
            Rectangle(MIRROR_3_COPY_1_SKETCH_W, MIRROR_3_COPY_1_SKETCH_H)
    revolve(axis=Axis((-701, -105, 622.35), (0, 0, 1)), mode=Mode.SUBTRACT)

    # 镜向3 copy 2 sketch → 镜向3 copy 2 (revolve, cut)
    with BuildSketch(Plane(origin=(-755, -159, 616), x_dir=(0, -1, 0), z_dir=(-1, 0, 0))):
        with Locations((1.05, -630.5)):
            Rectangle(MIRROR_3_COPY_2_SKETCH_W, MIRROR_3_COPY_2_SKETCH_H)
    revolve(axis=Axis((-755, -159, 622.35), (0, 0, 1)), mode=Mode.SUBTRACT)

    # 镜向3 copy 3 sketch → 镜向3 copy 3 (revolve, cut)
    with BuildSketch(Plane(origin=(-800, -159, 616), x_dir=(0, -1, 0), z_dir=(-1, 0, 0))):
        with Locations((1.05, -630.5)):
            Rectangle(MIRROR_3_COPY_3_SKETCH_W, MIRROR_3_COPY_3_SKETCH_H)
    revolve(axis=Axis((-800, -159, 622.35), (0, 0, 1)), mode=Mode.SUBTRACT)


solid = part.part
